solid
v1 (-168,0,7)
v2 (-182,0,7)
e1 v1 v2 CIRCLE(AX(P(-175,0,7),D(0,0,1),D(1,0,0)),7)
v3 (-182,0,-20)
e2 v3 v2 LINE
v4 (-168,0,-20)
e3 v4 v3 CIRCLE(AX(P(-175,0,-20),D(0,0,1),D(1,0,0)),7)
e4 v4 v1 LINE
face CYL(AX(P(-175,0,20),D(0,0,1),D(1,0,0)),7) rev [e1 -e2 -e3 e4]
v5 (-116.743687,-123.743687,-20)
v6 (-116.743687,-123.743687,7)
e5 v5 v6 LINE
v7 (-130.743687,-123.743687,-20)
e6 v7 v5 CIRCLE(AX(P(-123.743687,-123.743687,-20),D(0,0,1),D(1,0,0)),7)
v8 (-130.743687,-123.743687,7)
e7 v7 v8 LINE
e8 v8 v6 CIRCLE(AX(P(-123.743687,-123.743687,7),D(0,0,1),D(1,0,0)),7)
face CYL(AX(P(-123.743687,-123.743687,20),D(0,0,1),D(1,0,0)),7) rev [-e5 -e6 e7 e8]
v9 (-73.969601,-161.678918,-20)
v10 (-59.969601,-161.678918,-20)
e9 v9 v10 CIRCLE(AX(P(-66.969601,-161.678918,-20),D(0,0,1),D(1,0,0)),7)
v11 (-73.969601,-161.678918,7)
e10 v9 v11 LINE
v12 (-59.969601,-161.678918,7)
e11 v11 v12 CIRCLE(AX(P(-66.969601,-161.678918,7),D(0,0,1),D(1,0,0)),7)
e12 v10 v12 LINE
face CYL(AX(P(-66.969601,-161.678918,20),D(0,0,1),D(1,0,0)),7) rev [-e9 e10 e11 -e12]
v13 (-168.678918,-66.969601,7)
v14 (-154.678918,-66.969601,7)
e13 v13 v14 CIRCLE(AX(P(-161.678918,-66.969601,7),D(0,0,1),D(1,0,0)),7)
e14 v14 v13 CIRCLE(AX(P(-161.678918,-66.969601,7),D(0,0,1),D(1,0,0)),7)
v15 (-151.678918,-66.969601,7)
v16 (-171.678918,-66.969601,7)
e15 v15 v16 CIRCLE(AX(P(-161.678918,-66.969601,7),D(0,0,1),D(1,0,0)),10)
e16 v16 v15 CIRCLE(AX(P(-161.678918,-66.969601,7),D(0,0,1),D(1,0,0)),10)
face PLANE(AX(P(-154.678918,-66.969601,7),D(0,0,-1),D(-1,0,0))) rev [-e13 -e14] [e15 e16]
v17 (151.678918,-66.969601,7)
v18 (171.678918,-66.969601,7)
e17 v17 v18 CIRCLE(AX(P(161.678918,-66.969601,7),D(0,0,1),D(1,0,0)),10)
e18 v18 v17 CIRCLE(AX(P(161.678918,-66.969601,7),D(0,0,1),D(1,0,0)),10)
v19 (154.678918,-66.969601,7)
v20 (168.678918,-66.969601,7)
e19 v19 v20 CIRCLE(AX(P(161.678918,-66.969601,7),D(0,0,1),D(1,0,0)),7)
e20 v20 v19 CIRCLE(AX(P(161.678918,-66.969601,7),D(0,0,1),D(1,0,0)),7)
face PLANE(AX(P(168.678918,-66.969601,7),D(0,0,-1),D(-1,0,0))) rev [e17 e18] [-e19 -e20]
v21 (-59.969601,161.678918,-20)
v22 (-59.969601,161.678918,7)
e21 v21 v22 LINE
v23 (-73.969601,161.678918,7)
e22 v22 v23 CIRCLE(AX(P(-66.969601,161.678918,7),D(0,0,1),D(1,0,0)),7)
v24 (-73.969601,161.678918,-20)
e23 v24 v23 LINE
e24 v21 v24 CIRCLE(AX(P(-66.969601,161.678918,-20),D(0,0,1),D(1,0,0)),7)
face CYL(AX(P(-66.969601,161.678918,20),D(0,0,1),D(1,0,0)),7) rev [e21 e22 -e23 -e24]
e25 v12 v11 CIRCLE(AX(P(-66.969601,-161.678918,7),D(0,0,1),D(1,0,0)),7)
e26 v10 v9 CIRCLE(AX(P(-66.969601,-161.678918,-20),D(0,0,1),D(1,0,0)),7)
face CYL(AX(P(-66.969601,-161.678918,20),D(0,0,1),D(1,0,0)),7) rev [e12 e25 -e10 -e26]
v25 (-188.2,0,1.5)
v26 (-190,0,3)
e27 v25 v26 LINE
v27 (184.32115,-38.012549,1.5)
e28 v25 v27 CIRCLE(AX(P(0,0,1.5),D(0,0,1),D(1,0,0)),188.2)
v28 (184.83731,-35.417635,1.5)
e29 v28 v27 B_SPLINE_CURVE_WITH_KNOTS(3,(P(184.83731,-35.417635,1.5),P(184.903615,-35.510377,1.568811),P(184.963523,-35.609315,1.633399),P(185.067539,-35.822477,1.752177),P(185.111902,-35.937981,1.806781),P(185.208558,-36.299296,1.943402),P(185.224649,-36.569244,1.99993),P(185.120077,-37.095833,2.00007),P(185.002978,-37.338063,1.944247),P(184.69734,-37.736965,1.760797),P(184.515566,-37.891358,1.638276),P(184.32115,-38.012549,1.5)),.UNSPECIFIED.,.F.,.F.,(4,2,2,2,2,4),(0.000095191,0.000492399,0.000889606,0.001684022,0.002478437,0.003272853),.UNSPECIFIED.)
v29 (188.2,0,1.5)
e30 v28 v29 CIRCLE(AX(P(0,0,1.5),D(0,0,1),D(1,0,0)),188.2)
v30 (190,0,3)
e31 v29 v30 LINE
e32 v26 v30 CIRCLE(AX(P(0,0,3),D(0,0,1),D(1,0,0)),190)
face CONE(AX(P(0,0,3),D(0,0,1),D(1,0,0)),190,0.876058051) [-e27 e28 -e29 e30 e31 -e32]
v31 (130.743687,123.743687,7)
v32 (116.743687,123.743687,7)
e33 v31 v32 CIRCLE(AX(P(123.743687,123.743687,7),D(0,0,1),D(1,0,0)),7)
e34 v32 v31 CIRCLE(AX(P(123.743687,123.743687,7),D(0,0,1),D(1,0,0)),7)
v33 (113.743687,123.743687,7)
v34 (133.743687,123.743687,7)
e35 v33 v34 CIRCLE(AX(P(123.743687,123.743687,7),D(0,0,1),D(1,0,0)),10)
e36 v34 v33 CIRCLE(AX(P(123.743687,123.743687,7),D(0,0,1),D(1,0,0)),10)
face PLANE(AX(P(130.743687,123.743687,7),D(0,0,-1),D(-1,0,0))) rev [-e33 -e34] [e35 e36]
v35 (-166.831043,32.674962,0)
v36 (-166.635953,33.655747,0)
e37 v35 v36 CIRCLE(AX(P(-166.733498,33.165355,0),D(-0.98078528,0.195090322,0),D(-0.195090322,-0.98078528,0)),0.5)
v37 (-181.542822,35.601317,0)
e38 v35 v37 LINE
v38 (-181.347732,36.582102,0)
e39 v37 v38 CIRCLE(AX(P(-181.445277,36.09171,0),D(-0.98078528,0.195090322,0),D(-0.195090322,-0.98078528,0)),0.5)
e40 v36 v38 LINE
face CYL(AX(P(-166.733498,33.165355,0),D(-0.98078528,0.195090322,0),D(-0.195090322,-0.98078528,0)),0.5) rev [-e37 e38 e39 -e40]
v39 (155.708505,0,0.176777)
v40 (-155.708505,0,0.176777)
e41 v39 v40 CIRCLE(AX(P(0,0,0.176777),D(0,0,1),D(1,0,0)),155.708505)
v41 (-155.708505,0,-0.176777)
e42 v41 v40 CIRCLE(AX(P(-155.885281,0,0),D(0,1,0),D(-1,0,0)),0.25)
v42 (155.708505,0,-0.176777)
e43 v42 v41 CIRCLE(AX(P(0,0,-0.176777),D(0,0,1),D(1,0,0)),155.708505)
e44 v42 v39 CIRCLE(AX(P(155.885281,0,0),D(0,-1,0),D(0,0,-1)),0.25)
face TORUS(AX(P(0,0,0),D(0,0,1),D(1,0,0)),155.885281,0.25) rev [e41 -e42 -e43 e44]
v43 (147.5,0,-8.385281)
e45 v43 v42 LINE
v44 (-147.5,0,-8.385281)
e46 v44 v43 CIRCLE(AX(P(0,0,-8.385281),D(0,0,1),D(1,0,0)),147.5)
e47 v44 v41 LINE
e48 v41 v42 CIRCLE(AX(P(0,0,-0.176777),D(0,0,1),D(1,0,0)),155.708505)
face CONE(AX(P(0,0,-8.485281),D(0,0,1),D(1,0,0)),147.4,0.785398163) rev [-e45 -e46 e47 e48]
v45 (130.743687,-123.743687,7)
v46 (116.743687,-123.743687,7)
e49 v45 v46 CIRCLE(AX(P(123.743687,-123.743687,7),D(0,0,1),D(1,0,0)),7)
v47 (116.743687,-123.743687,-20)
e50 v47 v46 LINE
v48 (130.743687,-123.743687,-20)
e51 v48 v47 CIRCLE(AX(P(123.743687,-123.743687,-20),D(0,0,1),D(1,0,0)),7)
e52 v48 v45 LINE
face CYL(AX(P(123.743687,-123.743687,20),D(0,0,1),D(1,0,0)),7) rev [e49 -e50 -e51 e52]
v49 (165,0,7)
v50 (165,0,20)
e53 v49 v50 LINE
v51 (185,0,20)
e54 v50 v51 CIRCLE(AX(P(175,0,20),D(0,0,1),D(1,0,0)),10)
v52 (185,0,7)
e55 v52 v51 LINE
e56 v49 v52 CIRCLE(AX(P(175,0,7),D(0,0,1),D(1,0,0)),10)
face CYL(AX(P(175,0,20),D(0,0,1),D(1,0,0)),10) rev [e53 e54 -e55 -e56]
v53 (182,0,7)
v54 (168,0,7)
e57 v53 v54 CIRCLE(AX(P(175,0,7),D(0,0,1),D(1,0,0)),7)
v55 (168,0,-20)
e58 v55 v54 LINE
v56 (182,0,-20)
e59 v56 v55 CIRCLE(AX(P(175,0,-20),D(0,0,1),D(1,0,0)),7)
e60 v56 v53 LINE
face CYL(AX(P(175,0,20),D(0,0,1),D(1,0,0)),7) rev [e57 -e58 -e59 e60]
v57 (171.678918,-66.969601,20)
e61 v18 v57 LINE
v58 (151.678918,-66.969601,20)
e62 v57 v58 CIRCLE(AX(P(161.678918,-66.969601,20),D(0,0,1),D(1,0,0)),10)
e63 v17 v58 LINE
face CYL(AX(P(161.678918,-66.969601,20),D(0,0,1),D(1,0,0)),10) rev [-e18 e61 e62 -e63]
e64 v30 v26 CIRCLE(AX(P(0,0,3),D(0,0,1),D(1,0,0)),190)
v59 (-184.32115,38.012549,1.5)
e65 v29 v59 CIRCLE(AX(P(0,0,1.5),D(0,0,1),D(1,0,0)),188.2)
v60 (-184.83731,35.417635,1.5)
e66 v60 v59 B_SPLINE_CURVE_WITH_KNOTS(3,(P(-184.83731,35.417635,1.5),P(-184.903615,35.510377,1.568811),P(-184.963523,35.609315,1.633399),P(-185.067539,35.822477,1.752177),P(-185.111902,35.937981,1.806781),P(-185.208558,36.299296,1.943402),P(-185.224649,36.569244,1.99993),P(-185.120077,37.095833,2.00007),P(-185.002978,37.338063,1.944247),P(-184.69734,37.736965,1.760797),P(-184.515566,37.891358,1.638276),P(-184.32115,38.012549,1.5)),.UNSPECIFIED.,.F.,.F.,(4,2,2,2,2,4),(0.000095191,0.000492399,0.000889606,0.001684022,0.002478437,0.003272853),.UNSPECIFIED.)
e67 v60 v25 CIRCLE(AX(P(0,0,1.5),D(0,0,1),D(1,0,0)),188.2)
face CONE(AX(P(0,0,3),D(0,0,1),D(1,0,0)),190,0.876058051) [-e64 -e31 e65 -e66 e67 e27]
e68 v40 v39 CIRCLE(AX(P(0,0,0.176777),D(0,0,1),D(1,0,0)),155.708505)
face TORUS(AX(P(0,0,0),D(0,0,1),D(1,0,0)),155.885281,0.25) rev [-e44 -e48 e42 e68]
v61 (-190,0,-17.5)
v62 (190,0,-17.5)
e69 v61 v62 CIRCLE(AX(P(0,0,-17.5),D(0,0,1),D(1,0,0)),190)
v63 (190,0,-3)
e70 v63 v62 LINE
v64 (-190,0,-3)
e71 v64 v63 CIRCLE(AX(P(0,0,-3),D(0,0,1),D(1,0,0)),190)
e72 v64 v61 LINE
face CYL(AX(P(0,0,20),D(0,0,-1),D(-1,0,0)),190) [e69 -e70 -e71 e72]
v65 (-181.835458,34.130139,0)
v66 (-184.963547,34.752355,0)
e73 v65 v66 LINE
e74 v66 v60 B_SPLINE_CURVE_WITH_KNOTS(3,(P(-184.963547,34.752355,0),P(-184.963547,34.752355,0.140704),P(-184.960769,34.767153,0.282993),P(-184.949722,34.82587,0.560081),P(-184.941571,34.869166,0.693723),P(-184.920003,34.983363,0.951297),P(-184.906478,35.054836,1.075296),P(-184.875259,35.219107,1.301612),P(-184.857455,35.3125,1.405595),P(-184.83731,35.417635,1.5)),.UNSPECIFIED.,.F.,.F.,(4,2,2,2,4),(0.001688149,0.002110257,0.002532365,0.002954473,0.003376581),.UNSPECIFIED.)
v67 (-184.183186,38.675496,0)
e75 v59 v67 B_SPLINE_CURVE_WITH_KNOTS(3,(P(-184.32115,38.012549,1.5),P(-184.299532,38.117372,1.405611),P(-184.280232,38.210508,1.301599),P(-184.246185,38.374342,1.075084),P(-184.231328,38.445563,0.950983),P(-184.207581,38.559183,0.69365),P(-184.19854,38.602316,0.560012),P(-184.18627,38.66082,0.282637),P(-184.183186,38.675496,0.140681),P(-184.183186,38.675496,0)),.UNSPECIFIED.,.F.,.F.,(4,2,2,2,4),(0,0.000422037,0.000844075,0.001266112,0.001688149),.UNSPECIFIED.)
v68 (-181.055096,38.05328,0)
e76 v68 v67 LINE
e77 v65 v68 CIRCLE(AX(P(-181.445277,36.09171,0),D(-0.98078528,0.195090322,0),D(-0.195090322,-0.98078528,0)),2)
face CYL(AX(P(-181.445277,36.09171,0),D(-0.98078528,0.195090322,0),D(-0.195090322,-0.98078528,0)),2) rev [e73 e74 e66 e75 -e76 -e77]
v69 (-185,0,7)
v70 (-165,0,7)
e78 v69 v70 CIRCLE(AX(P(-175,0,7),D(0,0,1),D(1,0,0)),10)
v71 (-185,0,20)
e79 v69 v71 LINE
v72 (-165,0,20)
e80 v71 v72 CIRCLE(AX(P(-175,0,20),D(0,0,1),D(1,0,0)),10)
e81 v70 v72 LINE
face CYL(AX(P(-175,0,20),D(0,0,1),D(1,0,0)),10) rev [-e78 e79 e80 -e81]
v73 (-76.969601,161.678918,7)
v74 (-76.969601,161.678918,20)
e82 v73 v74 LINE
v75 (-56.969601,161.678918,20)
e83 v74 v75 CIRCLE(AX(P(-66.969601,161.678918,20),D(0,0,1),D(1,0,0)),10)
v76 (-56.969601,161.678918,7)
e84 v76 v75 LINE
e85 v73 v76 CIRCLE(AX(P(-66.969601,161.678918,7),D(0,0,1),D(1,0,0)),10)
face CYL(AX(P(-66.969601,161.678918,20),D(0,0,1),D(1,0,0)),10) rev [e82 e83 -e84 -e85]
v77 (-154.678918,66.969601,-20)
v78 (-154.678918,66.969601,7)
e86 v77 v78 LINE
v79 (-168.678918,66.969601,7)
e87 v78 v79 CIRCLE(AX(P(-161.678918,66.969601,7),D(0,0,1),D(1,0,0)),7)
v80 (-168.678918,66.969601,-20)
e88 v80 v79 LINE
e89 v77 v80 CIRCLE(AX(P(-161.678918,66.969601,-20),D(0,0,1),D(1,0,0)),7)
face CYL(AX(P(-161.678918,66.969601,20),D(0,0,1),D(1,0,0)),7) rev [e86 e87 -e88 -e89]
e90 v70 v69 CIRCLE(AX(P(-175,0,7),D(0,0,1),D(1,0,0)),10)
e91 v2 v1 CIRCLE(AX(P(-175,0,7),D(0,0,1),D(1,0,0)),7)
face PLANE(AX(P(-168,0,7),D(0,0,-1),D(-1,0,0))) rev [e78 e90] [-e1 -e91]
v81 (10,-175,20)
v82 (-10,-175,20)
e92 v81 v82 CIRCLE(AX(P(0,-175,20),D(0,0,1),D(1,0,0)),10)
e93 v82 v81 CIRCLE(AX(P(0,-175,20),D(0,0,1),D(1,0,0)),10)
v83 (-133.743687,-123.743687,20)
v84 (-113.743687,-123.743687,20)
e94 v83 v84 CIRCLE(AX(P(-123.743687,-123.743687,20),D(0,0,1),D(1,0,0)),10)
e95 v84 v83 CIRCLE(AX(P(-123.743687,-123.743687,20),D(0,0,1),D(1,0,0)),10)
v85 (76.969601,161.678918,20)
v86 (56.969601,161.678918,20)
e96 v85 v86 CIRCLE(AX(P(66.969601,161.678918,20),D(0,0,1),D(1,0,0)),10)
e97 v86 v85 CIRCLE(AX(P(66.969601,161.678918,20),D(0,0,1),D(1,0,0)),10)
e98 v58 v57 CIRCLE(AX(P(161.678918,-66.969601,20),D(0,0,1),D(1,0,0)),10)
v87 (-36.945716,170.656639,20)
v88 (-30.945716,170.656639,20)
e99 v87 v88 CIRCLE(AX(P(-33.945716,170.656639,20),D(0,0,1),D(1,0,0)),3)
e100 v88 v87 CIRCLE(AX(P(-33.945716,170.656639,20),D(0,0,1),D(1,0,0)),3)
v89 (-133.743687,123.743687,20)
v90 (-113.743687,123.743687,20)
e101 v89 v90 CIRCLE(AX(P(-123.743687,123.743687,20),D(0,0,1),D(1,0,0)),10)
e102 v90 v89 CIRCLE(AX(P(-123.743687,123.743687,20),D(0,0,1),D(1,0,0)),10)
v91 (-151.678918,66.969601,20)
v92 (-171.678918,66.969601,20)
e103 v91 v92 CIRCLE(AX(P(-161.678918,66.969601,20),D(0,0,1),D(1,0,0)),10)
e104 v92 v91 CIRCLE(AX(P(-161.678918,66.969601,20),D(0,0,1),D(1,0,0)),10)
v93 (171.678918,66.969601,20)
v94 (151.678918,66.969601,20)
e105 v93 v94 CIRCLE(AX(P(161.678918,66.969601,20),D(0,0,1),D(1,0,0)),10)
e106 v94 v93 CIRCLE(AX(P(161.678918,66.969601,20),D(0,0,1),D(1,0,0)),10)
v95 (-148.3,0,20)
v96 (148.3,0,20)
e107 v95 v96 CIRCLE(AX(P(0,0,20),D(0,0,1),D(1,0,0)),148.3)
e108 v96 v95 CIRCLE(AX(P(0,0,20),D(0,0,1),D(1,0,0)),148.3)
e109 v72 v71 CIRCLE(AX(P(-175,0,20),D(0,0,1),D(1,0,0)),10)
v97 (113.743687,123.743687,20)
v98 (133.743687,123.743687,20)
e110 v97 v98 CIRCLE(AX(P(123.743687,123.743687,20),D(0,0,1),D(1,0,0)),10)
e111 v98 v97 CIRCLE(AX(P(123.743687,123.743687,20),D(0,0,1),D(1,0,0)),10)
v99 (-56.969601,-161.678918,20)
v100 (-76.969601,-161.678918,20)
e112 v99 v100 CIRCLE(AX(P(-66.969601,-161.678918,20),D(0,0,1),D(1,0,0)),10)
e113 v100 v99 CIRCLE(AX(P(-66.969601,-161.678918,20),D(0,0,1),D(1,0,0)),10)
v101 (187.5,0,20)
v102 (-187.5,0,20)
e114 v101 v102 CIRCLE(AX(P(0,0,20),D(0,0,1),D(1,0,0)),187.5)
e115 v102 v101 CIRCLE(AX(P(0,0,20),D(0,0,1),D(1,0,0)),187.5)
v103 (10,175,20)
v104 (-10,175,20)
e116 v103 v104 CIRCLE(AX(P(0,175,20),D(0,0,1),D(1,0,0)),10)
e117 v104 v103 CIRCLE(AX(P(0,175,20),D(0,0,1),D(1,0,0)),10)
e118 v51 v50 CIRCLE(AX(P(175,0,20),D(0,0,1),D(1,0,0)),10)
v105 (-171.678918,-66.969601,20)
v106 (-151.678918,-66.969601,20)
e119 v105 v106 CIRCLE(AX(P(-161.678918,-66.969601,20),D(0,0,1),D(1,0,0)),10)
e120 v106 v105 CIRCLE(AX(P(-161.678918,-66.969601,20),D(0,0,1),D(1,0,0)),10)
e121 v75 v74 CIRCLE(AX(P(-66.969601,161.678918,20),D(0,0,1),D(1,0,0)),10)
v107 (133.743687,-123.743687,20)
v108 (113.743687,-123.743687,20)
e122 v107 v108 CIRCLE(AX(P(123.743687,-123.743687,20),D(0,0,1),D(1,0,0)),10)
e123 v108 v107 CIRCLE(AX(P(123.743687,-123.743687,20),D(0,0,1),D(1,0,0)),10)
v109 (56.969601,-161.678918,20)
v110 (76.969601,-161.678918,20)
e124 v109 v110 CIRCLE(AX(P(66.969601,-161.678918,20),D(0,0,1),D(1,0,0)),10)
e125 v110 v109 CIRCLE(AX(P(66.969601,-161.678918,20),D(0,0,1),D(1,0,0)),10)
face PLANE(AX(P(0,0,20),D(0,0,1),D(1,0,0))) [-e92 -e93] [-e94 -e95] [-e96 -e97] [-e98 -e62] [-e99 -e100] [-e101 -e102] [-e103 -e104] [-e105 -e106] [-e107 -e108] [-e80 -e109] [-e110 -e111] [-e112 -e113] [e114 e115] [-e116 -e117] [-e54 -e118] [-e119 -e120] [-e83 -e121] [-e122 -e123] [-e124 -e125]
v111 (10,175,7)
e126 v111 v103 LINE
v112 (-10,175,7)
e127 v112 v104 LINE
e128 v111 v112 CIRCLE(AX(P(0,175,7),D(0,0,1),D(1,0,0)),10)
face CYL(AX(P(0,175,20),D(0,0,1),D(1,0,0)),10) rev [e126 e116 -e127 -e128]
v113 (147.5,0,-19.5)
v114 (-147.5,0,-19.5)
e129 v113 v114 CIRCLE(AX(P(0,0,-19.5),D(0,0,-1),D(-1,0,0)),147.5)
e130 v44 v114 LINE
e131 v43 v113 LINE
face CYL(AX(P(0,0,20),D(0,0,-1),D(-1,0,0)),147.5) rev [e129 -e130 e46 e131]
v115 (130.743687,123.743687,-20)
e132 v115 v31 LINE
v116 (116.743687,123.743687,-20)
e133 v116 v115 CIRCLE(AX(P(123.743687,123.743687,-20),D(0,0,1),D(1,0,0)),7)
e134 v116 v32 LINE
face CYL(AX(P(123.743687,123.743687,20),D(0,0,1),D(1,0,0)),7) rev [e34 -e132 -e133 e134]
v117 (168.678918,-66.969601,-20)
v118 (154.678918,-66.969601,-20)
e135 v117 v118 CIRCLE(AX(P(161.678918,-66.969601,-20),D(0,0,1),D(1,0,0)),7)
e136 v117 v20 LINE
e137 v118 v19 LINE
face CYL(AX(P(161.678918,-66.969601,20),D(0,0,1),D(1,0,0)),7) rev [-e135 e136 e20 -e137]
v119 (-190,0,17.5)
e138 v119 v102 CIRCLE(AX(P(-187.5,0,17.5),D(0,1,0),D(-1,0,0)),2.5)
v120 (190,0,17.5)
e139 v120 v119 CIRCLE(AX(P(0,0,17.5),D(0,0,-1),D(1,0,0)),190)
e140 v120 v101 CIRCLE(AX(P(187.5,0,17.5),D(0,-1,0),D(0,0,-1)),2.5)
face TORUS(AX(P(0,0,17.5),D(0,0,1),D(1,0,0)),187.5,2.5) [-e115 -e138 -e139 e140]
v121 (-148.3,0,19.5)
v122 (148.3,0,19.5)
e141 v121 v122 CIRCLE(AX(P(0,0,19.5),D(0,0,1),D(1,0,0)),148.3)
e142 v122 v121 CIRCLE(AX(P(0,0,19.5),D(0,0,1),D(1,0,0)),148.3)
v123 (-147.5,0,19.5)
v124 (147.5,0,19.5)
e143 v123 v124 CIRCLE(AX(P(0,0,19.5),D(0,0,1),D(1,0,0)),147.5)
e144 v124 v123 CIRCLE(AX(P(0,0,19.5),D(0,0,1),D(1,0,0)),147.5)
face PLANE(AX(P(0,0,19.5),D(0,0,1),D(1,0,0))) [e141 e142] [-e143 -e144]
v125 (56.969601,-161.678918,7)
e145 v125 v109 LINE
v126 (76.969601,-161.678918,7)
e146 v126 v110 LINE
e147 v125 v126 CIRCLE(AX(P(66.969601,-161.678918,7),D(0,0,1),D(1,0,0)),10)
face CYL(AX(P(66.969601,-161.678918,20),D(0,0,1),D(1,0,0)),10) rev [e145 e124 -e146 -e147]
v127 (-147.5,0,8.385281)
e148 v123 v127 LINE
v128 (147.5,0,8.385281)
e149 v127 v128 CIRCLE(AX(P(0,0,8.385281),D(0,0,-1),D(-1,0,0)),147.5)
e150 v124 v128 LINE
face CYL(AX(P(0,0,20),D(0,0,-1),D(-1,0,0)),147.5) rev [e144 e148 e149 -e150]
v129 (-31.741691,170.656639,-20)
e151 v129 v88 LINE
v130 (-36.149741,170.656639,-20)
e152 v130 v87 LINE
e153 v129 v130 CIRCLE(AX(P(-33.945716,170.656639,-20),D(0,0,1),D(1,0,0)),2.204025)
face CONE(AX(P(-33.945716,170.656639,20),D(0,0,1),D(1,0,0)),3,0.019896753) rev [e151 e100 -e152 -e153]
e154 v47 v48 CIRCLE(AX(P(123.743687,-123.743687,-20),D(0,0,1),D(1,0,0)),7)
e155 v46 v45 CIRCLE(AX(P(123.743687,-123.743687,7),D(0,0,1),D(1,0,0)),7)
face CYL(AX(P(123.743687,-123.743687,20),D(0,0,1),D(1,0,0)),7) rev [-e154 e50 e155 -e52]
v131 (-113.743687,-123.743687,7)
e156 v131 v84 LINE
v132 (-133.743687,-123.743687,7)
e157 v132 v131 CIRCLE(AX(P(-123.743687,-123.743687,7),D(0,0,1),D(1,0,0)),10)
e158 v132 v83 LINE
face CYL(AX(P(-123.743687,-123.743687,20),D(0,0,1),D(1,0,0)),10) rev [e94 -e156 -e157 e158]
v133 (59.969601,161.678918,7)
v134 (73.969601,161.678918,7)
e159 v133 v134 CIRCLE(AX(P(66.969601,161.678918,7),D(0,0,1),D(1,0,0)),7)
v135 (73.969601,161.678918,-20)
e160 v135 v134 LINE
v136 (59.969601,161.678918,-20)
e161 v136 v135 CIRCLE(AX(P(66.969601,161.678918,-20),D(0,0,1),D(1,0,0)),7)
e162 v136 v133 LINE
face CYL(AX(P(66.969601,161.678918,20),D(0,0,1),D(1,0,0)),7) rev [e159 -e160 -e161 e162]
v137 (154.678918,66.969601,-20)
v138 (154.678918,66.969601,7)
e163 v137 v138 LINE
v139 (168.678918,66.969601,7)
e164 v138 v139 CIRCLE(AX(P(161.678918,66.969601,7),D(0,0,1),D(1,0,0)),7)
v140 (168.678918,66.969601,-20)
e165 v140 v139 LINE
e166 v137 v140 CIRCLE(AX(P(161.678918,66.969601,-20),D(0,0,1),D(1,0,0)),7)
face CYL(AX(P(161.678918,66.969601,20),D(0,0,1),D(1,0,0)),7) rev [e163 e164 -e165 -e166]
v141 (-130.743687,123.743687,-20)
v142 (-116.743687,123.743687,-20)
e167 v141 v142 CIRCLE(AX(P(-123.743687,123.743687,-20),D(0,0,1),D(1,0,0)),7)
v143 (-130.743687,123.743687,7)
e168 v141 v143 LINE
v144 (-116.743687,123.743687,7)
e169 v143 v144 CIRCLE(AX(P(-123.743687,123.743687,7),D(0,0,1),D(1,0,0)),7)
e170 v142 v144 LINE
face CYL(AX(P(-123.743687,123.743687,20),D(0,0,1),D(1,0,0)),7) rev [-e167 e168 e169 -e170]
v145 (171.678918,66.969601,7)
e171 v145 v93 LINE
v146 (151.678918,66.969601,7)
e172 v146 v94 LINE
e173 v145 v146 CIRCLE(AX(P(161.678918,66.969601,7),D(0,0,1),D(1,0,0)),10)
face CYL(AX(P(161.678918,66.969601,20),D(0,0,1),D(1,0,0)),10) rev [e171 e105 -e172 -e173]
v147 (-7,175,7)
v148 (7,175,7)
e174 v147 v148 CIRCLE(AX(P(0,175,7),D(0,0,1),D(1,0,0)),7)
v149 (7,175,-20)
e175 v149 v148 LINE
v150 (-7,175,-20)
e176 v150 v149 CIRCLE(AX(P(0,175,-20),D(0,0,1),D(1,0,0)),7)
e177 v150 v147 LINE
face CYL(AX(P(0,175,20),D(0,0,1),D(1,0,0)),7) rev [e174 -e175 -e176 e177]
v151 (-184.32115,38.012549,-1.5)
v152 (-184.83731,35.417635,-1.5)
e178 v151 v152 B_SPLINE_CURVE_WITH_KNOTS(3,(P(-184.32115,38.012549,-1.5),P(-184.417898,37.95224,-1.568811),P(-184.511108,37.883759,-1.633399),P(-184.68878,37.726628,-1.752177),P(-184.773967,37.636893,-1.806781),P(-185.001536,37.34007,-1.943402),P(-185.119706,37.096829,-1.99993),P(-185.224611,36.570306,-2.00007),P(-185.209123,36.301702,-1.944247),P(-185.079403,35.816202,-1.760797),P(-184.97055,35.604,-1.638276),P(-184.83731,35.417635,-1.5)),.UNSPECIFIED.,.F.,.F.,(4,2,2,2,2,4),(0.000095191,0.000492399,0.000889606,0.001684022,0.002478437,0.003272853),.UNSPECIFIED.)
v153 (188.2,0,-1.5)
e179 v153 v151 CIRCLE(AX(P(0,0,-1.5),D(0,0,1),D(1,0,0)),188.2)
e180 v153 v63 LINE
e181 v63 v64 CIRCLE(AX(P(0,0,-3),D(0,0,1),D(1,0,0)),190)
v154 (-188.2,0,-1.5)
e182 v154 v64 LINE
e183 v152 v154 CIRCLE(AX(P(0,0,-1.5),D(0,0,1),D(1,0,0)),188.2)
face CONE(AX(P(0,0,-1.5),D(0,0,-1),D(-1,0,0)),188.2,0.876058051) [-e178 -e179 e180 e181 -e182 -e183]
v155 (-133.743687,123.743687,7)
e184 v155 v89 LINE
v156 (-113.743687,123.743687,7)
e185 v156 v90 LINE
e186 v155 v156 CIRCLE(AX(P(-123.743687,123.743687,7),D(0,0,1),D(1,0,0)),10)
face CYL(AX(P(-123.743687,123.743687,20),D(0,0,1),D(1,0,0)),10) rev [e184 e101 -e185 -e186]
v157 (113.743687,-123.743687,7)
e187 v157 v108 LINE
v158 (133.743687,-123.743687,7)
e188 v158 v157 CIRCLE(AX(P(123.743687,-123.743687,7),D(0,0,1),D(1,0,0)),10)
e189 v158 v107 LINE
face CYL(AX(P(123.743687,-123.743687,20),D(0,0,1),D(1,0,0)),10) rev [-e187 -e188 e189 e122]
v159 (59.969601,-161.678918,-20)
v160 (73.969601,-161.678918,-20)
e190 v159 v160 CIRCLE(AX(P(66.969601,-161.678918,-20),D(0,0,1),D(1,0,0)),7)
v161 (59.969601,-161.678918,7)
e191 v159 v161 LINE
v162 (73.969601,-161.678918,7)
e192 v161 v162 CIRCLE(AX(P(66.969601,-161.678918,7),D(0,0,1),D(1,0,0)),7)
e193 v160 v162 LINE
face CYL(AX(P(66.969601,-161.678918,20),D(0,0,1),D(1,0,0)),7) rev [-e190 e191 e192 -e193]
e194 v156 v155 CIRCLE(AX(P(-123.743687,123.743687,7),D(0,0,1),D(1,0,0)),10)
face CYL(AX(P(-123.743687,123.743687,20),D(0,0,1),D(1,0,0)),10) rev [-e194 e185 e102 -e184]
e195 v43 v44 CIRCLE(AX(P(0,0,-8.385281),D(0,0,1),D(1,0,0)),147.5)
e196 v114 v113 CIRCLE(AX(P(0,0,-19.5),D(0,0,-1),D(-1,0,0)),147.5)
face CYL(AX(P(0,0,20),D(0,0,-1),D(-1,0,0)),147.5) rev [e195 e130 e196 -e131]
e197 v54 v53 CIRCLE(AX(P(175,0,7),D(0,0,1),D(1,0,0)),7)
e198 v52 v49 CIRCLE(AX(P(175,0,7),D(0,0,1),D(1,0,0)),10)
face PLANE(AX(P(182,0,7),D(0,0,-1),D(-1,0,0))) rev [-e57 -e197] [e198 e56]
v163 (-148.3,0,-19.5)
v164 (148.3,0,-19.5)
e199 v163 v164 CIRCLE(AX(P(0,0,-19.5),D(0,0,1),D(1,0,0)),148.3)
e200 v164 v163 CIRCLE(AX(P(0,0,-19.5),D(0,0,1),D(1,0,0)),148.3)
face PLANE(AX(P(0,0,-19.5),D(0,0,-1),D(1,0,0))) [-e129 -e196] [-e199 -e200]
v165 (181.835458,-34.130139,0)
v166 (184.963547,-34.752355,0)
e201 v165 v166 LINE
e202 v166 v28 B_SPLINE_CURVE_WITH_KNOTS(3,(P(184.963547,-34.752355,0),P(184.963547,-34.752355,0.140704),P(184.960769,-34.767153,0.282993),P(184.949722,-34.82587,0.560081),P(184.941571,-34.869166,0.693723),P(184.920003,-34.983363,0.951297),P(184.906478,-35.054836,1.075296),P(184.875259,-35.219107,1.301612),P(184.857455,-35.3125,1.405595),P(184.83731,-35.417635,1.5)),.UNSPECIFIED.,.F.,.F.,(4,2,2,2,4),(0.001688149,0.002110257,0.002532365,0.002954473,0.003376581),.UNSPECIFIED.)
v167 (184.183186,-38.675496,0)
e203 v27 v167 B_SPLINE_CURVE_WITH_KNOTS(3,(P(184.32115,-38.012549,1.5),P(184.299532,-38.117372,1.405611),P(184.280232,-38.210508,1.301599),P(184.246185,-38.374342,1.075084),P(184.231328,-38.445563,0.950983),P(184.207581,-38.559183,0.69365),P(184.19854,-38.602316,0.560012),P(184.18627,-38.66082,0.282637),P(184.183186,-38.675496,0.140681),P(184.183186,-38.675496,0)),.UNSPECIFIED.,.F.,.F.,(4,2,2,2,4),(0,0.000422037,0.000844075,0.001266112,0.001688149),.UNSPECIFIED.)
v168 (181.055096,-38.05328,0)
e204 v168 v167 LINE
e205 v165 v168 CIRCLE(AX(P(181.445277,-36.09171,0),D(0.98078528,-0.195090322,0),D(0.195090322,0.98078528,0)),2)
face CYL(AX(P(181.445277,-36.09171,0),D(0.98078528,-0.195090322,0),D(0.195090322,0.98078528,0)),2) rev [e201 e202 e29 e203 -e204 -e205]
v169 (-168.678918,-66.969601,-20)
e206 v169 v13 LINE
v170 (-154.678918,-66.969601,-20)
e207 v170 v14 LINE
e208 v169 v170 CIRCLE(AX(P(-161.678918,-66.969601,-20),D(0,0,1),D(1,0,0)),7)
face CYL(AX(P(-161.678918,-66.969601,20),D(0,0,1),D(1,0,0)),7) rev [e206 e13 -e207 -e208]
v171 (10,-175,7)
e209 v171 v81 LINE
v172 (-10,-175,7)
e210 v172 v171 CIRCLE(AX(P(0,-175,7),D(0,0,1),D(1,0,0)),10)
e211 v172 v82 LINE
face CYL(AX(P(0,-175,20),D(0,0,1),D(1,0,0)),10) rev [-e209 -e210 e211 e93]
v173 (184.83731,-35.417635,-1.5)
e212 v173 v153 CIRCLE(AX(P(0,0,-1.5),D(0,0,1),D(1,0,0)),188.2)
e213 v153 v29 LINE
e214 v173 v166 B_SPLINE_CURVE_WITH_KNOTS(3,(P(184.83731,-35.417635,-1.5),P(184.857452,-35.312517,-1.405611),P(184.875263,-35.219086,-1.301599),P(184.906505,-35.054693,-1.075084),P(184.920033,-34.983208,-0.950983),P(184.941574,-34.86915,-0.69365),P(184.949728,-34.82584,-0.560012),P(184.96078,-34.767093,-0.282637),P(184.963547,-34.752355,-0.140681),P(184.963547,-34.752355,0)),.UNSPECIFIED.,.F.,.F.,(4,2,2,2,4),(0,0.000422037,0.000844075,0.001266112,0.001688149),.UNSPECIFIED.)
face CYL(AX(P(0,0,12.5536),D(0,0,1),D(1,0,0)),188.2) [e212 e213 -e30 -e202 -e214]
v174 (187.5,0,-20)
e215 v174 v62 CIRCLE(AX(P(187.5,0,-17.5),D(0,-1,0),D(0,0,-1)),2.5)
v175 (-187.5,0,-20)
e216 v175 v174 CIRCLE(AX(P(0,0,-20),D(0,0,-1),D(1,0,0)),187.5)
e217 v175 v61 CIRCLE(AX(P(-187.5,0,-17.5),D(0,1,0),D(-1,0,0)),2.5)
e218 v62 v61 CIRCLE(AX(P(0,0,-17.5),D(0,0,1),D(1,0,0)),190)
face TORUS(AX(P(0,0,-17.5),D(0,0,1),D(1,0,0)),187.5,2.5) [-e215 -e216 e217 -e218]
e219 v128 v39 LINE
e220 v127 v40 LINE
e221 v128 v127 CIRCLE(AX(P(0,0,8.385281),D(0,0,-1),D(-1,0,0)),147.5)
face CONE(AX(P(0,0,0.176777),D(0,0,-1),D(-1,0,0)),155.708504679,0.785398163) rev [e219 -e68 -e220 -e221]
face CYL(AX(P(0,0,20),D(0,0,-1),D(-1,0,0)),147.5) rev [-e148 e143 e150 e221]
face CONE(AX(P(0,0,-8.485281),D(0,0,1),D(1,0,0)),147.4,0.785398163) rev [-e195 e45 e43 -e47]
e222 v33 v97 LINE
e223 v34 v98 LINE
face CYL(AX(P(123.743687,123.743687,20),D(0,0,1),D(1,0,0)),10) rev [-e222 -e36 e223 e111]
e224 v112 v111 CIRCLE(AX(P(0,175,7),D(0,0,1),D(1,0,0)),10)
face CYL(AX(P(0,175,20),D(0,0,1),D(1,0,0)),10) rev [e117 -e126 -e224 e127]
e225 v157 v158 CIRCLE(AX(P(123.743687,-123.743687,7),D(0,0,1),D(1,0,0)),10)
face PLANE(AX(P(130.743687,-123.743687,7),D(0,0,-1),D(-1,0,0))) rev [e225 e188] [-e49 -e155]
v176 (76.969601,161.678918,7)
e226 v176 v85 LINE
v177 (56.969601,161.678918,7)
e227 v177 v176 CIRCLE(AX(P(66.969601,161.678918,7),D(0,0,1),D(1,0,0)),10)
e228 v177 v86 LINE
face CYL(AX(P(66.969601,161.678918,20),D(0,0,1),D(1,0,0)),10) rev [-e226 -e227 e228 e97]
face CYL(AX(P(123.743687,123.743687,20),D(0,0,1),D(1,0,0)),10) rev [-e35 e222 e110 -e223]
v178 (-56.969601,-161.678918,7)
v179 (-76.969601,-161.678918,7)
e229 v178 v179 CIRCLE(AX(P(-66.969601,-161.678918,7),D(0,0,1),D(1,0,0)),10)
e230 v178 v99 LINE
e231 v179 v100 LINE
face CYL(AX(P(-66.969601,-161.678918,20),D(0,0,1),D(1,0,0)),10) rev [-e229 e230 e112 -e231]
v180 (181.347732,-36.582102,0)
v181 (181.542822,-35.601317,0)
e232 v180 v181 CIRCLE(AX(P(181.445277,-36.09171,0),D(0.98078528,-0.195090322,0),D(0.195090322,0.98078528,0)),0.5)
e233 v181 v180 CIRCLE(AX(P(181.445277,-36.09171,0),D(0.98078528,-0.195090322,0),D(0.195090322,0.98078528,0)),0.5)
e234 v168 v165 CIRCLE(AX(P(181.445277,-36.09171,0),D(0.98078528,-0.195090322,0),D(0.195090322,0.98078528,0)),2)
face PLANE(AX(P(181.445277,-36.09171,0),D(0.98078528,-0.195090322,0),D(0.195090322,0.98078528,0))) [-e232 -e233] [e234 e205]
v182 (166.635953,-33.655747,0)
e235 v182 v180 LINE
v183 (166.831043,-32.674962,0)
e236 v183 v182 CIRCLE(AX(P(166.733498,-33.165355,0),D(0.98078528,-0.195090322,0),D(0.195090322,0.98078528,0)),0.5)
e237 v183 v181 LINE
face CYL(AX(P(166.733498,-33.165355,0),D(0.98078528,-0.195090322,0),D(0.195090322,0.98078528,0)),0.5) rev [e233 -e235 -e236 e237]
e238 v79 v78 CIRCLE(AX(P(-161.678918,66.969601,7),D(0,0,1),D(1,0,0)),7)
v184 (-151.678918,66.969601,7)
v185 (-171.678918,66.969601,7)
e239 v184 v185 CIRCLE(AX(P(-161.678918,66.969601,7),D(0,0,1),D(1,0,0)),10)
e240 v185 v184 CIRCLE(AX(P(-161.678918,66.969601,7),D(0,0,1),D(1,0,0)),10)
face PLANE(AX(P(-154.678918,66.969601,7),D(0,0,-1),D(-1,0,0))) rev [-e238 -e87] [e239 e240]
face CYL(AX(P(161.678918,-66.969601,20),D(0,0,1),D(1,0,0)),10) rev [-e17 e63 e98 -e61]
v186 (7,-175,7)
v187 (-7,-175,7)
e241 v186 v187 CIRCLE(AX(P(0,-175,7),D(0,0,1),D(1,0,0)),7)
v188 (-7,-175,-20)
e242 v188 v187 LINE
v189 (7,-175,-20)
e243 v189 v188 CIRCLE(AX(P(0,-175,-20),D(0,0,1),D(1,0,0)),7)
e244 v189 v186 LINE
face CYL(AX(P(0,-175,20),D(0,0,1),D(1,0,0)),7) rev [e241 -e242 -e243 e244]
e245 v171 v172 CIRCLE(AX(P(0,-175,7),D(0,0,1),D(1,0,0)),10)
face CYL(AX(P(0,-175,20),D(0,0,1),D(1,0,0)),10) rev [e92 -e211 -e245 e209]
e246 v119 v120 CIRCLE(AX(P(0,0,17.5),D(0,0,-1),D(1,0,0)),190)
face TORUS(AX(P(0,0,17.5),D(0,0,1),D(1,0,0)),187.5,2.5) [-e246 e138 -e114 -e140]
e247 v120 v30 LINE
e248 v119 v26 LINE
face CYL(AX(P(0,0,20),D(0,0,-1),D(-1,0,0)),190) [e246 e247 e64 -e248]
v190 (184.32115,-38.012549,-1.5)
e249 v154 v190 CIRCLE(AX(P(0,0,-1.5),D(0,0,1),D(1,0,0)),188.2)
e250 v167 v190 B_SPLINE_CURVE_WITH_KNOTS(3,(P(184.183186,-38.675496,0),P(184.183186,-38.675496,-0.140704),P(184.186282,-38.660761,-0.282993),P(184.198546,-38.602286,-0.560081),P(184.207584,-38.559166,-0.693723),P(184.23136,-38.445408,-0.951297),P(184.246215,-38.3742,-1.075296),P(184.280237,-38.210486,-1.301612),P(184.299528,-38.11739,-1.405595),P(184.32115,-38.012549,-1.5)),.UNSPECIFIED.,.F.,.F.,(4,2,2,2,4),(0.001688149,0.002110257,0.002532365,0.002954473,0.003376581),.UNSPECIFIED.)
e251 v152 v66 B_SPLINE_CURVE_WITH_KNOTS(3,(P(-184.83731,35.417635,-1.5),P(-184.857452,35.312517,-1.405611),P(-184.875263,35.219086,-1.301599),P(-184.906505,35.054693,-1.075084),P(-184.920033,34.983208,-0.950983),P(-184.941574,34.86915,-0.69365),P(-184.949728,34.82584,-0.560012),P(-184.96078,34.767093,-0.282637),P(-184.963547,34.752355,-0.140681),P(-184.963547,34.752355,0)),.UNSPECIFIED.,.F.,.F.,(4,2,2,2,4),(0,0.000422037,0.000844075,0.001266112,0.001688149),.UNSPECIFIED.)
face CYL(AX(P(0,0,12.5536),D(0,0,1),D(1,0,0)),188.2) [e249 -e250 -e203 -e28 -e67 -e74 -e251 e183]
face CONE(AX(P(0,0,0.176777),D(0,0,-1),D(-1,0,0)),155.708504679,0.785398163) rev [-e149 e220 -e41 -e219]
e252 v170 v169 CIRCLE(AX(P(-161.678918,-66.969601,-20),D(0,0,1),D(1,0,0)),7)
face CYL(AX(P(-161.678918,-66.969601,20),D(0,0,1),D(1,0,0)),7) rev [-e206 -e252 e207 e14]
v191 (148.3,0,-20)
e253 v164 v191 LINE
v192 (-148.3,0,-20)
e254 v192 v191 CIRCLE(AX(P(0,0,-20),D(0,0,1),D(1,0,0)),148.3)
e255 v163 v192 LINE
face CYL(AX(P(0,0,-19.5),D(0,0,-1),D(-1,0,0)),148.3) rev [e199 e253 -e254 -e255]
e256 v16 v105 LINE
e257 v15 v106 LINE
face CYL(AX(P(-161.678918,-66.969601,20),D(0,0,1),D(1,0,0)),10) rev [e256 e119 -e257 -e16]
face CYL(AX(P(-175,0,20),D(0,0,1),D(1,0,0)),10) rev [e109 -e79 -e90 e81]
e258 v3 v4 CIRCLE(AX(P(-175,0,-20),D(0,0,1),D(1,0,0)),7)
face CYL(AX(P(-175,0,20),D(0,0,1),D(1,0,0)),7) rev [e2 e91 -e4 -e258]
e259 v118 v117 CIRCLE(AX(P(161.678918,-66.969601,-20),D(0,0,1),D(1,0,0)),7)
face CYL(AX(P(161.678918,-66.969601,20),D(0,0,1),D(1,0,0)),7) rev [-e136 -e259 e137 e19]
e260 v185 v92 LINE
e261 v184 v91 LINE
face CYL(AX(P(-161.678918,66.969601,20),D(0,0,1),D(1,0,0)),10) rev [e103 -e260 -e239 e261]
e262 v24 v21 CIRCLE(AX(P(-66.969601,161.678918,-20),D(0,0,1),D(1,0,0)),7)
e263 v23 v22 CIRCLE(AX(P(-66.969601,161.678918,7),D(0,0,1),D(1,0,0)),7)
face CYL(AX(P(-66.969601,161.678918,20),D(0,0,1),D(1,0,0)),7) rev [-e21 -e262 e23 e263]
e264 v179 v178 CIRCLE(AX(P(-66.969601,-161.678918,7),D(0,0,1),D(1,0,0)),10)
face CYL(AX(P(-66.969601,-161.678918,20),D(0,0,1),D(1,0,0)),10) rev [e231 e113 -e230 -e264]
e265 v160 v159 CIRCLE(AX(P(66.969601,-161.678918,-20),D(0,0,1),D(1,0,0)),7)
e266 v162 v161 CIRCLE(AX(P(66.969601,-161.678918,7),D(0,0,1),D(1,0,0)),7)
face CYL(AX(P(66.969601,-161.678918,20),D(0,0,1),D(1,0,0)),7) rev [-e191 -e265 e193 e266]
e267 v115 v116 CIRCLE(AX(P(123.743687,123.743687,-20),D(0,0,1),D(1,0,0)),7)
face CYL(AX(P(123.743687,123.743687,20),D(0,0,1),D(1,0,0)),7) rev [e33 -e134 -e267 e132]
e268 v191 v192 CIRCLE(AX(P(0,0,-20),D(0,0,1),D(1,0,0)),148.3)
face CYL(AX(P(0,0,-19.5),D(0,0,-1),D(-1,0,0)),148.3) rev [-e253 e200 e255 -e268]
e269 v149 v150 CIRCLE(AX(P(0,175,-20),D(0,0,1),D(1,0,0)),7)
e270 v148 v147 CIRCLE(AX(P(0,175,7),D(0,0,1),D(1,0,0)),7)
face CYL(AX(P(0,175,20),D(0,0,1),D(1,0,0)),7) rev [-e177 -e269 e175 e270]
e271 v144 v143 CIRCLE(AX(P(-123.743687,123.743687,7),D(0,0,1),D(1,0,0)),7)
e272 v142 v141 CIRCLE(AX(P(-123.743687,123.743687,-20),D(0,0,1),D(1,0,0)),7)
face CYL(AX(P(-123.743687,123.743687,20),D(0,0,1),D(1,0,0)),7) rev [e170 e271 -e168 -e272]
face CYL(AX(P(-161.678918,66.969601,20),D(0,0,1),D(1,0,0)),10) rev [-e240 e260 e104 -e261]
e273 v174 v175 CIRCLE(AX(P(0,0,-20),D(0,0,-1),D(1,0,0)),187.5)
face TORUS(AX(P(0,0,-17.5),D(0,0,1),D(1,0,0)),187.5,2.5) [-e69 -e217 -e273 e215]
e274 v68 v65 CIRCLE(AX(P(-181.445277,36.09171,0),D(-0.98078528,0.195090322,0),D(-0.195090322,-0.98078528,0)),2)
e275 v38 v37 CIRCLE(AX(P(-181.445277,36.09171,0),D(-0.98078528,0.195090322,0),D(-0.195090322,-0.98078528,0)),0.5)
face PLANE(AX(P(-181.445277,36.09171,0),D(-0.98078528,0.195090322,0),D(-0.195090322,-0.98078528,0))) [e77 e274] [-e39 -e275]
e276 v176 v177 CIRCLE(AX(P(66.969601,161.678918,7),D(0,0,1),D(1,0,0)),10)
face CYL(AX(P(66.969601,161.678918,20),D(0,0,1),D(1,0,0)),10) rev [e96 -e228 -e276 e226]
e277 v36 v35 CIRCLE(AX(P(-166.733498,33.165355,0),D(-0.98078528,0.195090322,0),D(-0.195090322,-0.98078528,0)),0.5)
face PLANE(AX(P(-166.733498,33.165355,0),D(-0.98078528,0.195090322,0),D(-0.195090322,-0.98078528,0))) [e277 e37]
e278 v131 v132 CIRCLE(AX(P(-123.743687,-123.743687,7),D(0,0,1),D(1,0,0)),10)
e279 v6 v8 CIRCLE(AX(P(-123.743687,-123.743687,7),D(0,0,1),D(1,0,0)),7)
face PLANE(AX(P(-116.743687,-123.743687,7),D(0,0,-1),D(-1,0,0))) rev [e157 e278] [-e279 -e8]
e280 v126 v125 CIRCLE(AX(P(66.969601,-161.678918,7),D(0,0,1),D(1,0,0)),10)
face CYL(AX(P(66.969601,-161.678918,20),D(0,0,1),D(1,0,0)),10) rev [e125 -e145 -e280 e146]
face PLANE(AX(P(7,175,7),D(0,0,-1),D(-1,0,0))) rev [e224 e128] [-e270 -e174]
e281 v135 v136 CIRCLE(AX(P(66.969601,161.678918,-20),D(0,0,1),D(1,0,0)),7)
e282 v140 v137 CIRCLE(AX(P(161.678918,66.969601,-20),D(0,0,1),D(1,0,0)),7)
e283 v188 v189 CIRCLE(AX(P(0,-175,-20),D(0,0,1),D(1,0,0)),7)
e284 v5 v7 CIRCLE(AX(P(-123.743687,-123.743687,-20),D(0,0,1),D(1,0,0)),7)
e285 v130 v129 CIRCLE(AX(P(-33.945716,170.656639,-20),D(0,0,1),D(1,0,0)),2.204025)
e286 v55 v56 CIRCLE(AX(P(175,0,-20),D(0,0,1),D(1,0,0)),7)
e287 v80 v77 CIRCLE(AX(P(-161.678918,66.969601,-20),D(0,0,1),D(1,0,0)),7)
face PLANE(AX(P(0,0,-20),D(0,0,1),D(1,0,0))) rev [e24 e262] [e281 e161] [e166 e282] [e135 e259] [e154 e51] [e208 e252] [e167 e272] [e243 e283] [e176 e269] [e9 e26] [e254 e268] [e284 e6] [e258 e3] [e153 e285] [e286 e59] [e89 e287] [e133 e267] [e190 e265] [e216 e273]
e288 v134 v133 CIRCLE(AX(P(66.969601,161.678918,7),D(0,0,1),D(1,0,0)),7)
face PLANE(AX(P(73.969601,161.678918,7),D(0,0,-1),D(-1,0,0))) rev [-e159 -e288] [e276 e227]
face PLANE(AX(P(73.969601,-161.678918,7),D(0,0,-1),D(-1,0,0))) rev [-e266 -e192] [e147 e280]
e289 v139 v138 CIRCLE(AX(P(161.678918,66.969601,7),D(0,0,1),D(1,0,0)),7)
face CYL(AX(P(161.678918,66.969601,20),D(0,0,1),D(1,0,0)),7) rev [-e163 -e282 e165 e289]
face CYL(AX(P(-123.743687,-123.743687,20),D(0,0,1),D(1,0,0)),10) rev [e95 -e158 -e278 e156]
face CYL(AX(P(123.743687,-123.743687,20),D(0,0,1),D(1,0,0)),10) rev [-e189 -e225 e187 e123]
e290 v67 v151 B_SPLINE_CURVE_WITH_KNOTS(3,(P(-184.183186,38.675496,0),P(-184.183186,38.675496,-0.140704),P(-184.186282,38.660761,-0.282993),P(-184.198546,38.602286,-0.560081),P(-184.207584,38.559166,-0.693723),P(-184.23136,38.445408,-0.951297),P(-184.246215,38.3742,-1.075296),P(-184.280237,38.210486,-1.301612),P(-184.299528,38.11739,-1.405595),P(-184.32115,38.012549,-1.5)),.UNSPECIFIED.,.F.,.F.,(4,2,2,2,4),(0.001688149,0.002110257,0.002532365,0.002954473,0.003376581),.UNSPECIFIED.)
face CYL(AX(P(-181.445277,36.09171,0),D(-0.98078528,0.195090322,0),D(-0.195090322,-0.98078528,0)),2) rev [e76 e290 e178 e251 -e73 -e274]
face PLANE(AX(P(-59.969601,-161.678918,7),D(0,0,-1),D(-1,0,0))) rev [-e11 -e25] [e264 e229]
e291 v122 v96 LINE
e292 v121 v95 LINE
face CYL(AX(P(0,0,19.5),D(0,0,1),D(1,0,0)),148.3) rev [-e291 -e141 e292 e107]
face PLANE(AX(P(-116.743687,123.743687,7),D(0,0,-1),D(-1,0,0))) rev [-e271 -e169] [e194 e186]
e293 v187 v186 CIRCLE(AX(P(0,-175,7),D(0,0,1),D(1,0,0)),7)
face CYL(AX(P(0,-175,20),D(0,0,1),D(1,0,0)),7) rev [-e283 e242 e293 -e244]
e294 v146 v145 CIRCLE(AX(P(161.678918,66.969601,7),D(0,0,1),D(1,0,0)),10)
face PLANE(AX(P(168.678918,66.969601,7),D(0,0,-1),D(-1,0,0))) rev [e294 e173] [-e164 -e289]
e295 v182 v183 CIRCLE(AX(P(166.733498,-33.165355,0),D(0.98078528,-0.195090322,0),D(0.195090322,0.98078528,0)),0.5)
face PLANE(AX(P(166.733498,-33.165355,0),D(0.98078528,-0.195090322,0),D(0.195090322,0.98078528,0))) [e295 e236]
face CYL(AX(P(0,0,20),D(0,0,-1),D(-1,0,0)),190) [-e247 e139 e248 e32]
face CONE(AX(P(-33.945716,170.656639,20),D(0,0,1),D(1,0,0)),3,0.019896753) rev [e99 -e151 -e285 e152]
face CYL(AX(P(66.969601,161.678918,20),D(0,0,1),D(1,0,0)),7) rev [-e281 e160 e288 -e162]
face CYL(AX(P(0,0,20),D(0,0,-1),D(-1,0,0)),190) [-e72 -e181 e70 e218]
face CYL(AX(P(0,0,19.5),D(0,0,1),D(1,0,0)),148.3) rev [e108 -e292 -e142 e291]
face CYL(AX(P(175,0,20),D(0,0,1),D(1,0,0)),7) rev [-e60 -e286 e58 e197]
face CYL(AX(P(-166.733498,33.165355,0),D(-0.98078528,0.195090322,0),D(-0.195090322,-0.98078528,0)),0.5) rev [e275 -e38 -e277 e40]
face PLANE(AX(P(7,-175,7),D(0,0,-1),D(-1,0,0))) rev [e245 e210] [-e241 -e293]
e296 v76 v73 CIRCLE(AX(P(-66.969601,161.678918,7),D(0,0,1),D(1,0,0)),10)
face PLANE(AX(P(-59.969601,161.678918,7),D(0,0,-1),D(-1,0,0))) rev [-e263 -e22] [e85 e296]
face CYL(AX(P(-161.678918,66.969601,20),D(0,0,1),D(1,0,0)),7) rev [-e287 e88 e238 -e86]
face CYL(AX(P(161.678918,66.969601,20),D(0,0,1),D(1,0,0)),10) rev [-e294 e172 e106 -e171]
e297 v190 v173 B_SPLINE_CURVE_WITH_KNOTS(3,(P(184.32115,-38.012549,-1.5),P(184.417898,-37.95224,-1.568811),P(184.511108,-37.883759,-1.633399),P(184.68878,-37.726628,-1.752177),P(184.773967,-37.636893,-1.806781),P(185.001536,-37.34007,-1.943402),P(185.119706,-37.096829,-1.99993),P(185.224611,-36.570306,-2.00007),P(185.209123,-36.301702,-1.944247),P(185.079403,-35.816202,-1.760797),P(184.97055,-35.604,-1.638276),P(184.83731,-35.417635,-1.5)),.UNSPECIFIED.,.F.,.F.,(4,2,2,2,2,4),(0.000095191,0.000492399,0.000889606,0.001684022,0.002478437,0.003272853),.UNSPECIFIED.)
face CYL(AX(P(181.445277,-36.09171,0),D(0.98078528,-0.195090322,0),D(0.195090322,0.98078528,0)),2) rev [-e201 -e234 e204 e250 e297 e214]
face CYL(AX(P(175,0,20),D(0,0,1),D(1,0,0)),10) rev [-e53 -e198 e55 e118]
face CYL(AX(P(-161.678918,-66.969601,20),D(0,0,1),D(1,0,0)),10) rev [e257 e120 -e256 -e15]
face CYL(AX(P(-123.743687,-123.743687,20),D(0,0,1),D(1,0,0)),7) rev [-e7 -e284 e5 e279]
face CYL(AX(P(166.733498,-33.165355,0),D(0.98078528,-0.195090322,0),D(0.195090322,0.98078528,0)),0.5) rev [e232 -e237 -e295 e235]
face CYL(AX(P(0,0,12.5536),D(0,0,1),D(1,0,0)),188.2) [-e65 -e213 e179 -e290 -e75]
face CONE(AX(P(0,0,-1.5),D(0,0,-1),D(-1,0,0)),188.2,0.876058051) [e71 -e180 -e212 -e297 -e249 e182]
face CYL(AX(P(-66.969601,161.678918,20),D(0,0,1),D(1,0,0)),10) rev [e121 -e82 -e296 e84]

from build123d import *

# Parameters (mm, degrees)
SKETCH_1_R                     = 190
SKETCH_1_R_2                   = 147.5
EXTRUDE_1_DEPTH                = 20
FILLET_1_R                     = 2.5
HOLE_WIZARD_M1_6_1_D           = 14
HOLE_WIZARD_M1_6_1_CBORE_D     = 20
HOLE_WIZARD_M1_6_1_CBORE_DEPTH = 13
PATTERN_CIRCULAR_1_COUNT       = 16
CUT_EXTRUDE_START              = 190
SKETCH_7_R                     = 2
CUT_EXTRUDE_1_DEPTH            = 5
SKETCH_8_R                     = 0.5
CUT_EXTRUDE_2_DEPTH            = 15
PATTERN_CIRCULAR_2_COUNT       = 2
SKETCH_9_R                     = 148.3
CUT_EXTRUDE_3_DEPTH            = 0.5


with BuildPart() as part:
    # 草图1 → 凸台-拉伸1 (new, symmetric)
    with BuildSketch(Plane.XY):
        Circle(SKETCH_1_R)
        Circle(SKETCH_1_R_2, mode=Mode.SUBTRACT)
    extrude(amount=EXTRUDE_1_DEPTH, both=True)

    # 草图2 → 切除-旋转1 (revolve, cut)
    with BuildSketch(Plane(origin=(0, 0, 0), x_dir=(0, 0, -1), z_dir=(1, 0, 0)), mode=Mode.PRIVATE) as cut_revolve_1_sk:
        with BuildLine():
            Line((-8.485281374, 147.4), (-0.176776695, 155.708504679))
            ThreePointArc((-0.176776695, 155.708504679), (0, 156.135281374), (0.176776695, 155.708504679))
            Line((0.176776695, 155.708504679), (8.485281374, 147.4))
            Line((8.485281374, 147.4), (-8.485281374, 147.4))
        make_face()
        Polygon((-3, 190), (3, 190), (1.5, 188.2), (-1.5, 188.2), align=None)
    revolve(cut_revolve_1_sk.sketch.rotate(Axis((0, 0, 12.553599724), (0, 0, -1)), 90), axis=Axis((0, 0, 12.553599724), (0, 0, -1)), mode=Mode.SUBTRACT)

    # 圆角1
    fillet_1_edges = [part.edges().sort_by_distance(p)[0] for p in [
        (-190, 0, -20),
        (-190, 0, 20),
    ]]
    fillet(fillet_1_edges, radius=FILLET_1_R)

    # M1.6 六角头螺栓的柱形沉头孔1 (through all)
    with Locations(Plane.XY.offset(20)):
        with Locations((0, 175)):
            hole_wizard_m1_6_1 = CounterBoreHole(HOLE_WIZARD_M1_6_1_D / 2, HOLE_WIZARD_M1_6_1_CBORE_D / 2, HOLE_WIZARD_M1_6_1_CBORE_DEPTH)

    # 阵列(圆周)1: M1.6 六角头螺栓的柱形沉头孔1 ×16 about axis
    pattern_circular_1_axis = Axis((0, 0, 0), (0, 0, 1))
    for i in range(1, PATTERN_CIRCULAR_1_COUNT):
        add(hole_wizard_m1_6_1.rotate(pattern_circular_1_axis, i * 360 / PATTERN_CIRCULAR_1_COUNT), mode=Mode.SUBTRACT)

    # 草图7 → 切除-拉伸1 (cut)
    with BuildSketch(Plane(origin=(0, 0, 0), x_dir=(0, 0, -1), z_dir=(0.9807852804032297, -0.19509032201613213, 0)).offset(CUT_EXTRUDE_START)):
        with Locations(Location((0, 0, 0), (0, 0, 90))):
            Circle(SKETCH_7_R)
    cut_extrude_1 = extrude(amount=-CUT_EXTRUDE_1_DEPTH, mode=Mode.SUBTRACT)

    # 草图8 → 切除-拉伸2 (cut)
    with BuildSketch(Plane(origin=(181.445276875, -36.091709573, 0), x_dir=(-0.19509032201613213, -0.9807852804032298, 0), z_dir=(0.9807852804032297, -0.1950903220161321, 0))):
        with Locations(Location((0, 0, 0), (0, 0, 180))):
            Circle(SKETCH_8_R)
    cut_extrude_2 = extrude(amount=-CUT_EXTRUDE_2_DEPTH, mode=Mode.SUBTRACT)

    # 阵列(圆周)2: 切除-拉伸1, 切除-拉伸2 ×2 about axis
    pattern_circular_2_axis = Axis((0, 0, 20), (0, 0, -1))
    add([cut_extrude_1.rotate(pattern_circular_2_axis, i * 360 / PATTERN_CIRCULAR_2_COUNT) for i in range(1, PATTERN_CIRCULAR_2_COUNT)], mode=Mode.SUBTRACT)
    add([cut_extrude_2.rotate(pattern_circular_2_axis, i * 360 / PATTERN_CIRCULAR_2_COUNT) for i in range(1, PATTERN_CIRCULAR_2_COUNT)], mode=Mode.SUBTRACT)

    # 草图9 → 切除-拉伸3 (cut)
    with BuildSketch(Plane.XY.offset(20)):
        Circle(SKETCH_9_R)
    cut_extrude_3 = extrude(amount=-CUT_EXTRUDE_3_DEPTH, mode=Mode.SUBTRACT)

    # 镜向1: 切除-拉伸3 across plane
    add(cut_extrude_3.mirror(Plane.XY), mode=Mode.SUBTRACT)

    # 切除-拉伸4 cone 1 section (through the dimple's axis) → 切除-拉伸4 (revolve, cut)
    with BuildSketch(Plane(origin=(-33.945716031, 170.65663879, 20), x_dir=(0, -1, 0), z_dir=(1, 0, 0))):
        Polygon((0, 0), (3, 0), (0, 150.758469861), align=None)
    revolve(axis=Axis((-33.945716031, 170.65663879, 20), (0, 0, -1)), mode=Mode.SUBTRACT)


solid = part.part
